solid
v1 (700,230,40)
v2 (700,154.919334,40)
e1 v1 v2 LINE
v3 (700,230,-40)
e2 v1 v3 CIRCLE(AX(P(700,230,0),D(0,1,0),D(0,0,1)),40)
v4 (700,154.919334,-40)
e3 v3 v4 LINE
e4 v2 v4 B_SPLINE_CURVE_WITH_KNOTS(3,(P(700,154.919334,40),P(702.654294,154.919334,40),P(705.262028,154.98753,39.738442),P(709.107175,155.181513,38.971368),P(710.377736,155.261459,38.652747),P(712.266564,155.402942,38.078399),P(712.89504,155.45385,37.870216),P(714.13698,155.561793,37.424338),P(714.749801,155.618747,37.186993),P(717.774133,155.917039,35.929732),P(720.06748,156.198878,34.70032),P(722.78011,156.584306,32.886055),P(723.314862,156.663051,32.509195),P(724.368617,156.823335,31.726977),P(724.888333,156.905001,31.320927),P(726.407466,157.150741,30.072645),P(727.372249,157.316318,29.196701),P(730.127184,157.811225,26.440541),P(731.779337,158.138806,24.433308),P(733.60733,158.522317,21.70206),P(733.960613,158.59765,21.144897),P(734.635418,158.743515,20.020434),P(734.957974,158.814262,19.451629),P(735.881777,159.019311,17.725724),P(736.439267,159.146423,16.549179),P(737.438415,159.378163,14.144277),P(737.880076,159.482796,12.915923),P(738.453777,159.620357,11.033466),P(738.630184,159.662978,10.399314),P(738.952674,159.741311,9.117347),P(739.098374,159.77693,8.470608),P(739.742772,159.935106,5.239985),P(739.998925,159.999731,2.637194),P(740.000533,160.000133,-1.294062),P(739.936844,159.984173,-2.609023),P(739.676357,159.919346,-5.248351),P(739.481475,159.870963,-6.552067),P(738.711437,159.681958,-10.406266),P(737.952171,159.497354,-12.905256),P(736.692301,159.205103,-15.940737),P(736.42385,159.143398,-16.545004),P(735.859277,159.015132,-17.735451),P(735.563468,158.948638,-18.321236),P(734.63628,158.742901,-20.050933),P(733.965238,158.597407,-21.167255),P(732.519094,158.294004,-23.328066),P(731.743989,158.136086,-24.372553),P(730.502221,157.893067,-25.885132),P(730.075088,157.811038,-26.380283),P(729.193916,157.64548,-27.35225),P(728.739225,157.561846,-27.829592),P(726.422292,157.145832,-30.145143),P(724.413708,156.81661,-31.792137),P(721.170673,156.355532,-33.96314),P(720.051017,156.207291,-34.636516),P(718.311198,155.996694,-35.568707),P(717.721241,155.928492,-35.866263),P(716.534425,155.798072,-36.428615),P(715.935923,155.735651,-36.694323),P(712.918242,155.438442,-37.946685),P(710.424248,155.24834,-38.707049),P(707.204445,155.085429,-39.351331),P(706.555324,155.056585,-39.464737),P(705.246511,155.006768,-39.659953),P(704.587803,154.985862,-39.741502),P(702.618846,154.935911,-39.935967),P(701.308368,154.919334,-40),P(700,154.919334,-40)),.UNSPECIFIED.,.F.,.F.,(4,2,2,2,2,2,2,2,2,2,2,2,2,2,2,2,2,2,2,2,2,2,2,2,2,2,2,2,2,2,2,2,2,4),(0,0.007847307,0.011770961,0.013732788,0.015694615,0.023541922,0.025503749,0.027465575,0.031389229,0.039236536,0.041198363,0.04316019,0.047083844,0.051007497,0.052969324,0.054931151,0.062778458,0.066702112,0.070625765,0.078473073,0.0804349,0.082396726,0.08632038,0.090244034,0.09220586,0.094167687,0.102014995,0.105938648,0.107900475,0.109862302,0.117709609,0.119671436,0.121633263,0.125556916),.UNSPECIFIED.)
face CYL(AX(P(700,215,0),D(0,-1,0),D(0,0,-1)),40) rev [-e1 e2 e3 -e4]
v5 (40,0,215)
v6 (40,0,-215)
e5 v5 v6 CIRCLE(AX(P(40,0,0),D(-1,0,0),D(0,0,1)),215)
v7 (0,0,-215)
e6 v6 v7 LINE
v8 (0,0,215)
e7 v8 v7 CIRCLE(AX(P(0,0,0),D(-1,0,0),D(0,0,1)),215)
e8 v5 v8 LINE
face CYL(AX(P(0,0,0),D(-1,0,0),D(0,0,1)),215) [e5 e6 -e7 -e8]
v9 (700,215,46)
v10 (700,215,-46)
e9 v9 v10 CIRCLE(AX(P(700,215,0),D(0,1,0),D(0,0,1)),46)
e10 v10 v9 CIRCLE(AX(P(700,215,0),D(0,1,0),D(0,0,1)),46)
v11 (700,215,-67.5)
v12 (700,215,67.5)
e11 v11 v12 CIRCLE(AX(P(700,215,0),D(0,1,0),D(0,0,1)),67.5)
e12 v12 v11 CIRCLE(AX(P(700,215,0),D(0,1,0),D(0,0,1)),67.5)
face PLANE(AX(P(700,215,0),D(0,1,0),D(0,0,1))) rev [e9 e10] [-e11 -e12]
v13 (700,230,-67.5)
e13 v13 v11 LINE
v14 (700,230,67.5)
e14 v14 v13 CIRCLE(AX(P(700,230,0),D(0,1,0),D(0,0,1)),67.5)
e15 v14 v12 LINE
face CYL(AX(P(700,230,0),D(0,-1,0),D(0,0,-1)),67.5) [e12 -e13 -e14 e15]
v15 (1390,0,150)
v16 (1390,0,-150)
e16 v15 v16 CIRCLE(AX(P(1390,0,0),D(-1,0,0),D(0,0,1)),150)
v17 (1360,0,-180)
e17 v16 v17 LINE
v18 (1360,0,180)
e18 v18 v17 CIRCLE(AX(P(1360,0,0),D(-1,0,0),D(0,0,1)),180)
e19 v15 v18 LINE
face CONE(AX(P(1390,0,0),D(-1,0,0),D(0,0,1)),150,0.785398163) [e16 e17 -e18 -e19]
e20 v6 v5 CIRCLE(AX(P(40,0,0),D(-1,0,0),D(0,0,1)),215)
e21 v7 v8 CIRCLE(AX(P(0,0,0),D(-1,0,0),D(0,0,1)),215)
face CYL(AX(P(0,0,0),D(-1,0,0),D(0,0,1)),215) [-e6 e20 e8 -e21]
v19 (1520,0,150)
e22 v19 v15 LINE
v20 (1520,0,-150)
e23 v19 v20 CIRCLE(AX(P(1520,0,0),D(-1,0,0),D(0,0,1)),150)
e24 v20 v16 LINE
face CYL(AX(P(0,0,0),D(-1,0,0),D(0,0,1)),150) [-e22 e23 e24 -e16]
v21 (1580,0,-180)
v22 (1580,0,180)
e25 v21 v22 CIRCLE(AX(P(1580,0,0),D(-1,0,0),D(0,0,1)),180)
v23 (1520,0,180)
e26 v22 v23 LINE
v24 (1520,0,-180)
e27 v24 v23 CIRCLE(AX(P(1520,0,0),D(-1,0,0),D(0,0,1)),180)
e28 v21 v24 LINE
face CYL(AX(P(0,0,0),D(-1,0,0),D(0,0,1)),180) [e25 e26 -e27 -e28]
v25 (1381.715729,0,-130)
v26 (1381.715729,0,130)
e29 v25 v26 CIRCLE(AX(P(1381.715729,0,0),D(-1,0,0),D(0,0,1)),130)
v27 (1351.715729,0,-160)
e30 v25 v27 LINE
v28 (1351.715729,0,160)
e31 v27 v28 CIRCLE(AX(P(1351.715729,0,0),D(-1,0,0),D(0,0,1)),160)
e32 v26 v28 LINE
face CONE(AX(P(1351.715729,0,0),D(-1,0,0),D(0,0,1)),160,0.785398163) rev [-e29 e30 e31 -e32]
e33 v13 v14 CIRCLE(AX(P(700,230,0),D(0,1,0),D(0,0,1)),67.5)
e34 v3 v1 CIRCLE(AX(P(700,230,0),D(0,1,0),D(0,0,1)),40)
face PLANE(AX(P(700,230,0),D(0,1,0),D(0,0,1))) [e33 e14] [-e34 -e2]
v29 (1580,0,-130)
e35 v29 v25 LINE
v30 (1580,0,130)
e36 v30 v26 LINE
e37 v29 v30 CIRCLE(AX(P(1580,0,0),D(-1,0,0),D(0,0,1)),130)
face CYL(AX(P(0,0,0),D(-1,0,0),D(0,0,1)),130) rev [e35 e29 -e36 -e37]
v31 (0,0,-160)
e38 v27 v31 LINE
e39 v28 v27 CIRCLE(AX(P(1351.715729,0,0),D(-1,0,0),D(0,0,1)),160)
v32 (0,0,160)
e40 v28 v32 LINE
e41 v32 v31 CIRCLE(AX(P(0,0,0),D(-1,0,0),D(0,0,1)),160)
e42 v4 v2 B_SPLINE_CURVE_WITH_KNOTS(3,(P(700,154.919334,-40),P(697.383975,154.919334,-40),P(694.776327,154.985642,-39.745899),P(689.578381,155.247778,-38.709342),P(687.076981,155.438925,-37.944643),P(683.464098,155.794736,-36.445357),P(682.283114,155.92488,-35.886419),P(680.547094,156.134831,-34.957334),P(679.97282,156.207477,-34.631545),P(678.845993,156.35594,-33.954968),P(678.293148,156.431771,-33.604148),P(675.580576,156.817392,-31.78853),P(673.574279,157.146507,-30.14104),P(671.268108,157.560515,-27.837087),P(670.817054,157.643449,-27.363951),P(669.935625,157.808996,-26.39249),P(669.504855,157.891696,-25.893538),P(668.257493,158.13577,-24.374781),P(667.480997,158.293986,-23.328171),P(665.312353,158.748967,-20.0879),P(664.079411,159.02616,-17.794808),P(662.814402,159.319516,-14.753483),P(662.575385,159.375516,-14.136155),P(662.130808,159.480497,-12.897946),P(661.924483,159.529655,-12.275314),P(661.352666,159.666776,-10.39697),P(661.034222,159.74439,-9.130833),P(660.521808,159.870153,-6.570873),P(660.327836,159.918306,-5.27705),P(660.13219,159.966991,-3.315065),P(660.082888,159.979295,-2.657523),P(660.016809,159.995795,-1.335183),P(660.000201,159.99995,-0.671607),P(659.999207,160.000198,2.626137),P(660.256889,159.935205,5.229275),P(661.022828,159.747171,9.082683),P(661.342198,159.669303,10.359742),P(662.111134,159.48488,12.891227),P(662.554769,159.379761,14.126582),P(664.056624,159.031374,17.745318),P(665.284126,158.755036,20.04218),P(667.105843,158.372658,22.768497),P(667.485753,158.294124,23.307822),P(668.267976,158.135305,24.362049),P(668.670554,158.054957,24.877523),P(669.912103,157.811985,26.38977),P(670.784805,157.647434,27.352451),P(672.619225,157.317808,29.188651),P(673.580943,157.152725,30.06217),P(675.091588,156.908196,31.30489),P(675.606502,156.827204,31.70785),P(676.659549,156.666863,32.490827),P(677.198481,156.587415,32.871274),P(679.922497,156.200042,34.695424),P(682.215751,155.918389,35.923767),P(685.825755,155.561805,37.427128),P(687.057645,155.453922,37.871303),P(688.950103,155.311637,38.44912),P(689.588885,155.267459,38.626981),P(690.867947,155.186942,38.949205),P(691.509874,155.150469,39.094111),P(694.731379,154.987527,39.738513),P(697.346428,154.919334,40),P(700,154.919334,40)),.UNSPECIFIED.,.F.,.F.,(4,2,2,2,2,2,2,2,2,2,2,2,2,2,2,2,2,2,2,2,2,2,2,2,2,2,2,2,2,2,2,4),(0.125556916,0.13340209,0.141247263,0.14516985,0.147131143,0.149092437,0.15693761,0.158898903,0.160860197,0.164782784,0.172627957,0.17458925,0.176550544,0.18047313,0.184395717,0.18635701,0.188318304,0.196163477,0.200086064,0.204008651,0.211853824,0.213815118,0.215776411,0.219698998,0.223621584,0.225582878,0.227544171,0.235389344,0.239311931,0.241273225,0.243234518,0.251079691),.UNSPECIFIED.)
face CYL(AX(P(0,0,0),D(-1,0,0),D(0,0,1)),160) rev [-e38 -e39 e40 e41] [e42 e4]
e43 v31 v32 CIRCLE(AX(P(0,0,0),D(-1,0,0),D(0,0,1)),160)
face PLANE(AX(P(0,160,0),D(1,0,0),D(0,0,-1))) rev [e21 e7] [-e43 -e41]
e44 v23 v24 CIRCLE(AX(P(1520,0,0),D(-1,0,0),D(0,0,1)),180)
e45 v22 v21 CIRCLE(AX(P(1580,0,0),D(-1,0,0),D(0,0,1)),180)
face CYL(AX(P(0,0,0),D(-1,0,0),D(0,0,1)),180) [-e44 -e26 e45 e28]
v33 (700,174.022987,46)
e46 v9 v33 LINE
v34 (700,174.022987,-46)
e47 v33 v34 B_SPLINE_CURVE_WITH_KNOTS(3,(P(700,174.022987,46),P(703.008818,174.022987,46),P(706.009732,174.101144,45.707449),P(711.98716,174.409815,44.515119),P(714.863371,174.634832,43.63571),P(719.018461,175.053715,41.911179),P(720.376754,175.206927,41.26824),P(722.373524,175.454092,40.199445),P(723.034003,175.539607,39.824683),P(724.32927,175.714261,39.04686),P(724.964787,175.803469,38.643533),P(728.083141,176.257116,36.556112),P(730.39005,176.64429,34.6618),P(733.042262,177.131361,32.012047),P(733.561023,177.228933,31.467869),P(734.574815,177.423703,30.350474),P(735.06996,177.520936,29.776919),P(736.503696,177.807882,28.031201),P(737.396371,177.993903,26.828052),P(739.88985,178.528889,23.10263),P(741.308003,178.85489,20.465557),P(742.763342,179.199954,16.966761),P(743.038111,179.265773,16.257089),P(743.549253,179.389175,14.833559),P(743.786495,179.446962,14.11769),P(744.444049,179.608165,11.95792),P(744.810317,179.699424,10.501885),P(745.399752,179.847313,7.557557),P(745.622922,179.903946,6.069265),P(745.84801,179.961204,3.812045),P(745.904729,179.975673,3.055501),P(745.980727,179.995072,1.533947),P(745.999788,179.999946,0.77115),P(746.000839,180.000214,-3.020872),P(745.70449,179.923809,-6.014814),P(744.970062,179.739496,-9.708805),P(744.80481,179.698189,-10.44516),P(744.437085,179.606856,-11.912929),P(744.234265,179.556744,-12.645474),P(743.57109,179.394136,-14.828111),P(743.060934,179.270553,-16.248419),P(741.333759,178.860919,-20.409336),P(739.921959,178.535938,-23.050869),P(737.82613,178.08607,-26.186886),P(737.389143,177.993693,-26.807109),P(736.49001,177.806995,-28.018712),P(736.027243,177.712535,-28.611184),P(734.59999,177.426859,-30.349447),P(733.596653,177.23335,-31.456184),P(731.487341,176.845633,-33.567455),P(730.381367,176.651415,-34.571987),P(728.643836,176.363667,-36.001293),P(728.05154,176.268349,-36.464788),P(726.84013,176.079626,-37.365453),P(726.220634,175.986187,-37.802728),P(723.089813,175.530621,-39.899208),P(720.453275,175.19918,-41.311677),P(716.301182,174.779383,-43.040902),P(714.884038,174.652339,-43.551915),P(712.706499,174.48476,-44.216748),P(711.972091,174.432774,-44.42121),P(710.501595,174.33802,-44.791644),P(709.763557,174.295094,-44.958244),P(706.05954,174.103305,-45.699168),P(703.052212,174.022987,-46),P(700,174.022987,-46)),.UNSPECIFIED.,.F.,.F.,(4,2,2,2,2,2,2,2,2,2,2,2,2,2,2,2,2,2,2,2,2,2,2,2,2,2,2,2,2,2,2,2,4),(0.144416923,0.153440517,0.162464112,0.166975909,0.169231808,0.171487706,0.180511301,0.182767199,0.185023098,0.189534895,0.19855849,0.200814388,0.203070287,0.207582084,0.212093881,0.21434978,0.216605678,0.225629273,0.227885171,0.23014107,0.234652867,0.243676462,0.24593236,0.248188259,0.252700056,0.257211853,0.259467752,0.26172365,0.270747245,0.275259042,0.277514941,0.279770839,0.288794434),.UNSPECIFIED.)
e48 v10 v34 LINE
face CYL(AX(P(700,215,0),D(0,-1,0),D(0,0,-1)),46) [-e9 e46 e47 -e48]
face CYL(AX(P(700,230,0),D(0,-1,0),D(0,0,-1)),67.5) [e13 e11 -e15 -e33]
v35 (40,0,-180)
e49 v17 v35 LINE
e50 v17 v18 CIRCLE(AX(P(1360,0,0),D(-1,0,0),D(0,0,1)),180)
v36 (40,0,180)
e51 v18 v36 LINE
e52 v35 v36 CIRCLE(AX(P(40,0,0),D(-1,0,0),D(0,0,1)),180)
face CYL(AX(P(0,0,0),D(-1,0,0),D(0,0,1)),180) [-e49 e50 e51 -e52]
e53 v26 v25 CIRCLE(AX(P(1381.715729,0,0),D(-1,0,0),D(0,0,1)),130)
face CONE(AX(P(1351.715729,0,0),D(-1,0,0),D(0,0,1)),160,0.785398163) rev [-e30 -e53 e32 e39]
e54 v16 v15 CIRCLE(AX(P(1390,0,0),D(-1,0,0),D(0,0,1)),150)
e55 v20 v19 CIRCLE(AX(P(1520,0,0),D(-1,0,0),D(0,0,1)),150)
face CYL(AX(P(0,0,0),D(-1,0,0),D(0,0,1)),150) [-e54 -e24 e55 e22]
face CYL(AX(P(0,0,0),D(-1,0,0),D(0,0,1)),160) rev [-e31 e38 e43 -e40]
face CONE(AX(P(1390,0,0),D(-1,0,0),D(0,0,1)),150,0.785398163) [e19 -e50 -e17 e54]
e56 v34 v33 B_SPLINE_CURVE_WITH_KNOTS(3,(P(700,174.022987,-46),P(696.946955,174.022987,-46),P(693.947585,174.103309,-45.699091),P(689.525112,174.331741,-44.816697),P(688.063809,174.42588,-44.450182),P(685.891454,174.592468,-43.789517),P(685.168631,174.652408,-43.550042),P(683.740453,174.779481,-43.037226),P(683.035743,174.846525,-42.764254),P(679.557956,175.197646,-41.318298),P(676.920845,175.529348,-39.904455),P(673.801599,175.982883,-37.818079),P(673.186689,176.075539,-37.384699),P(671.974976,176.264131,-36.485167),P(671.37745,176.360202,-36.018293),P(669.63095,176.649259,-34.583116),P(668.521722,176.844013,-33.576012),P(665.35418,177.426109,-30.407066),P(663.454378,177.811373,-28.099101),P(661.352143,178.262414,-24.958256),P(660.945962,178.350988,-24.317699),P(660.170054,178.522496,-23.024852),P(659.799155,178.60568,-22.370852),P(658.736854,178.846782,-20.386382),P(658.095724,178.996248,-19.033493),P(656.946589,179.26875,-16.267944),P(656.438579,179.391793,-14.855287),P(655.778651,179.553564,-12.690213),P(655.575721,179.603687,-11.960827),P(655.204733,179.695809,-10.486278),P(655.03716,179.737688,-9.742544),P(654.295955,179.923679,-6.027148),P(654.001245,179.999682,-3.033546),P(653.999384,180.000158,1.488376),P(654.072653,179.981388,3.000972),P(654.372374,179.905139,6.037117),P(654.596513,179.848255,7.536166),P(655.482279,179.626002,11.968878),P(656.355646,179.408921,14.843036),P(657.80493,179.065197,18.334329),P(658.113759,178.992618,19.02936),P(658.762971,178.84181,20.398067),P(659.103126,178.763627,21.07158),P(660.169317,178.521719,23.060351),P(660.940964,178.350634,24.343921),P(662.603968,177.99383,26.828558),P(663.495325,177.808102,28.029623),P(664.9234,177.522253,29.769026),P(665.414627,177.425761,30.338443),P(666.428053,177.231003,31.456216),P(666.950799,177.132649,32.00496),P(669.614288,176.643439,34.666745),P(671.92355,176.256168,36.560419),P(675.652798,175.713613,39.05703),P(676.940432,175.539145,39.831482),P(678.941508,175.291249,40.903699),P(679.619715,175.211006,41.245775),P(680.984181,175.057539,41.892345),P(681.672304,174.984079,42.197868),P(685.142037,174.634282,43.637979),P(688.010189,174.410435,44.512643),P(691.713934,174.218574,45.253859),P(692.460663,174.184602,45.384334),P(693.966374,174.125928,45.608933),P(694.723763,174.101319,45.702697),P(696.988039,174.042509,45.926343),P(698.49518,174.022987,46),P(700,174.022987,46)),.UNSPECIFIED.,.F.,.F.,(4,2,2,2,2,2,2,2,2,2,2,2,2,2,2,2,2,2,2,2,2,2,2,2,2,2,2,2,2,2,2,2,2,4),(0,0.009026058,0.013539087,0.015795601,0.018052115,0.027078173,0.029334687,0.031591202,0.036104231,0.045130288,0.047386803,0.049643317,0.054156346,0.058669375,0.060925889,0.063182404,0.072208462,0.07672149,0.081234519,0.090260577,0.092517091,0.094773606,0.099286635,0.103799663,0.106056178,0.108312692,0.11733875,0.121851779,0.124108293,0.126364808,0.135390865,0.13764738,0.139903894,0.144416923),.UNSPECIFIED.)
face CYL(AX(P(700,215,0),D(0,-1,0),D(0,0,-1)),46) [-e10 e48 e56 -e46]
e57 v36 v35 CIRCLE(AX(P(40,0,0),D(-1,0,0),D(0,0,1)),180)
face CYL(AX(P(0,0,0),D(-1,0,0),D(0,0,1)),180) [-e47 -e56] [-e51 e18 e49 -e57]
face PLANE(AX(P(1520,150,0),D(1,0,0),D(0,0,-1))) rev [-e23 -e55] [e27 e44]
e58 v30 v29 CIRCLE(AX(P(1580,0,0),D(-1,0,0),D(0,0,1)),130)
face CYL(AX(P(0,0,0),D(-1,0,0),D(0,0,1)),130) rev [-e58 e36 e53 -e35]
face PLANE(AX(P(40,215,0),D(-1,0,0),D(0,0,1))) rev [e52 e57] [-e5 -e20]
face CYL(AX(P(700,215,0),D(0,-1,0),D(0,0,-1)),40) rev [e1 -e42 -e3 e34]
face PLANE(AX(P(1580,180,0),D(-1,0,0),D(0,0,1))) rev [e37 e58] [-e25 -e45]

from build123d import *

# Parameters (mm, degrees)
SKETCH3_R           = 46
SKETCH3_R_2         = 40
BOSS_EXTRUDE1_DEPTH = 215
SKETCH4_R           = 160
CUT_EXTRUDE1_DEPTH  = 900
CUT_EXTRUDE2_START  = -300
SKETCH5_R           = 40
CUT_EXTRUDE2_DEPTH  = 300
SKETCH6_R           = 67.5
SKETCH6_R_2         = 40
BOSS_EXTRUDE2_DEPTH = 15


with BuildPart() as part:
    # Sketch1 → Revolve1 (revolve)
    with BuildSketch(Plane.XY, mode=Mode.PRIVATE) as revolve1_sk:
        Polygon((0, 160), (0, 215), (40, 215), (40, 180), (1360, 180), (1390, 150), (1520, 150), (1520, 180), (1580, 180), (1580, 130), (1381.715728753, 130), (1351.715728753, 160), align=None)
    revolve(revolve1_sk.sketch.rotate(Axis((0, 0, 0), (1, 0, 0)), 90), axis=Axis((0, 0, 0), (1, 0, 0)))

    # Sketch3 → Boss-Extrude1 (add)
    with BuildSketch(Plane(origin=(0, 0, 0), x_dir=(1, 0, 0), z_dir=(0, 1, 0))):
        with Locations(Location((700, 0, 0), (0, 0, 90))):
            Circle(SKETCH3_R)
        with Locations(Location((700, 0, 0), (0, 0, 90))):
            Circle(SKETCH3_R_2, mode=Mode.SUBTRACT)
    extrude(amount=BOSS_EXTRUDE1_DEPTH)

    # Sketch4 → Cut-Extrude1 (cut)
    with BuildSketch(Plane.ZY):
        Circle(SKETCH4_R)
    extrude(amount=-CUT_EXTRUDE1_DEPTH, mode=Mode.SUBTRACT)

    # Sketch5 → Cut-Extrude2 (cut)
    with BuildSketch(Plane(origin=(0, 215, 0), x_dir=(1, 0, 0), z_dir=(0, 1, 0)).offset(CUT_EXTRUDE2_START)):
        with Locations(Location((700, 0, 0), (0, 0, 270))):
            Circle(SKETCH5_R)
    extrude(amount=CUT_EXTRUDE2_DEPTH, mode=Mode.SUBTRACT)

    # Sketch6 → Boss-Extrude2 (add)
    with BuildSketch(Plane(origin=(0, 215, 0), x_dir=(1, 0, 0), z_dir=(0, 1, 0))):
        with Locations(Location((700, 0, 0), (0, 0, 270))):
            Circle(SKETCH6_R)
        with Locations(Location((700, 0, 0), (0, 0, 270))):
            Circle(SKETCH6_R_2, mode=Mode.SUBTRACT)
    extrude(amount=BOSS_EXTRUDE2_DEPTH)


solid = part.part
